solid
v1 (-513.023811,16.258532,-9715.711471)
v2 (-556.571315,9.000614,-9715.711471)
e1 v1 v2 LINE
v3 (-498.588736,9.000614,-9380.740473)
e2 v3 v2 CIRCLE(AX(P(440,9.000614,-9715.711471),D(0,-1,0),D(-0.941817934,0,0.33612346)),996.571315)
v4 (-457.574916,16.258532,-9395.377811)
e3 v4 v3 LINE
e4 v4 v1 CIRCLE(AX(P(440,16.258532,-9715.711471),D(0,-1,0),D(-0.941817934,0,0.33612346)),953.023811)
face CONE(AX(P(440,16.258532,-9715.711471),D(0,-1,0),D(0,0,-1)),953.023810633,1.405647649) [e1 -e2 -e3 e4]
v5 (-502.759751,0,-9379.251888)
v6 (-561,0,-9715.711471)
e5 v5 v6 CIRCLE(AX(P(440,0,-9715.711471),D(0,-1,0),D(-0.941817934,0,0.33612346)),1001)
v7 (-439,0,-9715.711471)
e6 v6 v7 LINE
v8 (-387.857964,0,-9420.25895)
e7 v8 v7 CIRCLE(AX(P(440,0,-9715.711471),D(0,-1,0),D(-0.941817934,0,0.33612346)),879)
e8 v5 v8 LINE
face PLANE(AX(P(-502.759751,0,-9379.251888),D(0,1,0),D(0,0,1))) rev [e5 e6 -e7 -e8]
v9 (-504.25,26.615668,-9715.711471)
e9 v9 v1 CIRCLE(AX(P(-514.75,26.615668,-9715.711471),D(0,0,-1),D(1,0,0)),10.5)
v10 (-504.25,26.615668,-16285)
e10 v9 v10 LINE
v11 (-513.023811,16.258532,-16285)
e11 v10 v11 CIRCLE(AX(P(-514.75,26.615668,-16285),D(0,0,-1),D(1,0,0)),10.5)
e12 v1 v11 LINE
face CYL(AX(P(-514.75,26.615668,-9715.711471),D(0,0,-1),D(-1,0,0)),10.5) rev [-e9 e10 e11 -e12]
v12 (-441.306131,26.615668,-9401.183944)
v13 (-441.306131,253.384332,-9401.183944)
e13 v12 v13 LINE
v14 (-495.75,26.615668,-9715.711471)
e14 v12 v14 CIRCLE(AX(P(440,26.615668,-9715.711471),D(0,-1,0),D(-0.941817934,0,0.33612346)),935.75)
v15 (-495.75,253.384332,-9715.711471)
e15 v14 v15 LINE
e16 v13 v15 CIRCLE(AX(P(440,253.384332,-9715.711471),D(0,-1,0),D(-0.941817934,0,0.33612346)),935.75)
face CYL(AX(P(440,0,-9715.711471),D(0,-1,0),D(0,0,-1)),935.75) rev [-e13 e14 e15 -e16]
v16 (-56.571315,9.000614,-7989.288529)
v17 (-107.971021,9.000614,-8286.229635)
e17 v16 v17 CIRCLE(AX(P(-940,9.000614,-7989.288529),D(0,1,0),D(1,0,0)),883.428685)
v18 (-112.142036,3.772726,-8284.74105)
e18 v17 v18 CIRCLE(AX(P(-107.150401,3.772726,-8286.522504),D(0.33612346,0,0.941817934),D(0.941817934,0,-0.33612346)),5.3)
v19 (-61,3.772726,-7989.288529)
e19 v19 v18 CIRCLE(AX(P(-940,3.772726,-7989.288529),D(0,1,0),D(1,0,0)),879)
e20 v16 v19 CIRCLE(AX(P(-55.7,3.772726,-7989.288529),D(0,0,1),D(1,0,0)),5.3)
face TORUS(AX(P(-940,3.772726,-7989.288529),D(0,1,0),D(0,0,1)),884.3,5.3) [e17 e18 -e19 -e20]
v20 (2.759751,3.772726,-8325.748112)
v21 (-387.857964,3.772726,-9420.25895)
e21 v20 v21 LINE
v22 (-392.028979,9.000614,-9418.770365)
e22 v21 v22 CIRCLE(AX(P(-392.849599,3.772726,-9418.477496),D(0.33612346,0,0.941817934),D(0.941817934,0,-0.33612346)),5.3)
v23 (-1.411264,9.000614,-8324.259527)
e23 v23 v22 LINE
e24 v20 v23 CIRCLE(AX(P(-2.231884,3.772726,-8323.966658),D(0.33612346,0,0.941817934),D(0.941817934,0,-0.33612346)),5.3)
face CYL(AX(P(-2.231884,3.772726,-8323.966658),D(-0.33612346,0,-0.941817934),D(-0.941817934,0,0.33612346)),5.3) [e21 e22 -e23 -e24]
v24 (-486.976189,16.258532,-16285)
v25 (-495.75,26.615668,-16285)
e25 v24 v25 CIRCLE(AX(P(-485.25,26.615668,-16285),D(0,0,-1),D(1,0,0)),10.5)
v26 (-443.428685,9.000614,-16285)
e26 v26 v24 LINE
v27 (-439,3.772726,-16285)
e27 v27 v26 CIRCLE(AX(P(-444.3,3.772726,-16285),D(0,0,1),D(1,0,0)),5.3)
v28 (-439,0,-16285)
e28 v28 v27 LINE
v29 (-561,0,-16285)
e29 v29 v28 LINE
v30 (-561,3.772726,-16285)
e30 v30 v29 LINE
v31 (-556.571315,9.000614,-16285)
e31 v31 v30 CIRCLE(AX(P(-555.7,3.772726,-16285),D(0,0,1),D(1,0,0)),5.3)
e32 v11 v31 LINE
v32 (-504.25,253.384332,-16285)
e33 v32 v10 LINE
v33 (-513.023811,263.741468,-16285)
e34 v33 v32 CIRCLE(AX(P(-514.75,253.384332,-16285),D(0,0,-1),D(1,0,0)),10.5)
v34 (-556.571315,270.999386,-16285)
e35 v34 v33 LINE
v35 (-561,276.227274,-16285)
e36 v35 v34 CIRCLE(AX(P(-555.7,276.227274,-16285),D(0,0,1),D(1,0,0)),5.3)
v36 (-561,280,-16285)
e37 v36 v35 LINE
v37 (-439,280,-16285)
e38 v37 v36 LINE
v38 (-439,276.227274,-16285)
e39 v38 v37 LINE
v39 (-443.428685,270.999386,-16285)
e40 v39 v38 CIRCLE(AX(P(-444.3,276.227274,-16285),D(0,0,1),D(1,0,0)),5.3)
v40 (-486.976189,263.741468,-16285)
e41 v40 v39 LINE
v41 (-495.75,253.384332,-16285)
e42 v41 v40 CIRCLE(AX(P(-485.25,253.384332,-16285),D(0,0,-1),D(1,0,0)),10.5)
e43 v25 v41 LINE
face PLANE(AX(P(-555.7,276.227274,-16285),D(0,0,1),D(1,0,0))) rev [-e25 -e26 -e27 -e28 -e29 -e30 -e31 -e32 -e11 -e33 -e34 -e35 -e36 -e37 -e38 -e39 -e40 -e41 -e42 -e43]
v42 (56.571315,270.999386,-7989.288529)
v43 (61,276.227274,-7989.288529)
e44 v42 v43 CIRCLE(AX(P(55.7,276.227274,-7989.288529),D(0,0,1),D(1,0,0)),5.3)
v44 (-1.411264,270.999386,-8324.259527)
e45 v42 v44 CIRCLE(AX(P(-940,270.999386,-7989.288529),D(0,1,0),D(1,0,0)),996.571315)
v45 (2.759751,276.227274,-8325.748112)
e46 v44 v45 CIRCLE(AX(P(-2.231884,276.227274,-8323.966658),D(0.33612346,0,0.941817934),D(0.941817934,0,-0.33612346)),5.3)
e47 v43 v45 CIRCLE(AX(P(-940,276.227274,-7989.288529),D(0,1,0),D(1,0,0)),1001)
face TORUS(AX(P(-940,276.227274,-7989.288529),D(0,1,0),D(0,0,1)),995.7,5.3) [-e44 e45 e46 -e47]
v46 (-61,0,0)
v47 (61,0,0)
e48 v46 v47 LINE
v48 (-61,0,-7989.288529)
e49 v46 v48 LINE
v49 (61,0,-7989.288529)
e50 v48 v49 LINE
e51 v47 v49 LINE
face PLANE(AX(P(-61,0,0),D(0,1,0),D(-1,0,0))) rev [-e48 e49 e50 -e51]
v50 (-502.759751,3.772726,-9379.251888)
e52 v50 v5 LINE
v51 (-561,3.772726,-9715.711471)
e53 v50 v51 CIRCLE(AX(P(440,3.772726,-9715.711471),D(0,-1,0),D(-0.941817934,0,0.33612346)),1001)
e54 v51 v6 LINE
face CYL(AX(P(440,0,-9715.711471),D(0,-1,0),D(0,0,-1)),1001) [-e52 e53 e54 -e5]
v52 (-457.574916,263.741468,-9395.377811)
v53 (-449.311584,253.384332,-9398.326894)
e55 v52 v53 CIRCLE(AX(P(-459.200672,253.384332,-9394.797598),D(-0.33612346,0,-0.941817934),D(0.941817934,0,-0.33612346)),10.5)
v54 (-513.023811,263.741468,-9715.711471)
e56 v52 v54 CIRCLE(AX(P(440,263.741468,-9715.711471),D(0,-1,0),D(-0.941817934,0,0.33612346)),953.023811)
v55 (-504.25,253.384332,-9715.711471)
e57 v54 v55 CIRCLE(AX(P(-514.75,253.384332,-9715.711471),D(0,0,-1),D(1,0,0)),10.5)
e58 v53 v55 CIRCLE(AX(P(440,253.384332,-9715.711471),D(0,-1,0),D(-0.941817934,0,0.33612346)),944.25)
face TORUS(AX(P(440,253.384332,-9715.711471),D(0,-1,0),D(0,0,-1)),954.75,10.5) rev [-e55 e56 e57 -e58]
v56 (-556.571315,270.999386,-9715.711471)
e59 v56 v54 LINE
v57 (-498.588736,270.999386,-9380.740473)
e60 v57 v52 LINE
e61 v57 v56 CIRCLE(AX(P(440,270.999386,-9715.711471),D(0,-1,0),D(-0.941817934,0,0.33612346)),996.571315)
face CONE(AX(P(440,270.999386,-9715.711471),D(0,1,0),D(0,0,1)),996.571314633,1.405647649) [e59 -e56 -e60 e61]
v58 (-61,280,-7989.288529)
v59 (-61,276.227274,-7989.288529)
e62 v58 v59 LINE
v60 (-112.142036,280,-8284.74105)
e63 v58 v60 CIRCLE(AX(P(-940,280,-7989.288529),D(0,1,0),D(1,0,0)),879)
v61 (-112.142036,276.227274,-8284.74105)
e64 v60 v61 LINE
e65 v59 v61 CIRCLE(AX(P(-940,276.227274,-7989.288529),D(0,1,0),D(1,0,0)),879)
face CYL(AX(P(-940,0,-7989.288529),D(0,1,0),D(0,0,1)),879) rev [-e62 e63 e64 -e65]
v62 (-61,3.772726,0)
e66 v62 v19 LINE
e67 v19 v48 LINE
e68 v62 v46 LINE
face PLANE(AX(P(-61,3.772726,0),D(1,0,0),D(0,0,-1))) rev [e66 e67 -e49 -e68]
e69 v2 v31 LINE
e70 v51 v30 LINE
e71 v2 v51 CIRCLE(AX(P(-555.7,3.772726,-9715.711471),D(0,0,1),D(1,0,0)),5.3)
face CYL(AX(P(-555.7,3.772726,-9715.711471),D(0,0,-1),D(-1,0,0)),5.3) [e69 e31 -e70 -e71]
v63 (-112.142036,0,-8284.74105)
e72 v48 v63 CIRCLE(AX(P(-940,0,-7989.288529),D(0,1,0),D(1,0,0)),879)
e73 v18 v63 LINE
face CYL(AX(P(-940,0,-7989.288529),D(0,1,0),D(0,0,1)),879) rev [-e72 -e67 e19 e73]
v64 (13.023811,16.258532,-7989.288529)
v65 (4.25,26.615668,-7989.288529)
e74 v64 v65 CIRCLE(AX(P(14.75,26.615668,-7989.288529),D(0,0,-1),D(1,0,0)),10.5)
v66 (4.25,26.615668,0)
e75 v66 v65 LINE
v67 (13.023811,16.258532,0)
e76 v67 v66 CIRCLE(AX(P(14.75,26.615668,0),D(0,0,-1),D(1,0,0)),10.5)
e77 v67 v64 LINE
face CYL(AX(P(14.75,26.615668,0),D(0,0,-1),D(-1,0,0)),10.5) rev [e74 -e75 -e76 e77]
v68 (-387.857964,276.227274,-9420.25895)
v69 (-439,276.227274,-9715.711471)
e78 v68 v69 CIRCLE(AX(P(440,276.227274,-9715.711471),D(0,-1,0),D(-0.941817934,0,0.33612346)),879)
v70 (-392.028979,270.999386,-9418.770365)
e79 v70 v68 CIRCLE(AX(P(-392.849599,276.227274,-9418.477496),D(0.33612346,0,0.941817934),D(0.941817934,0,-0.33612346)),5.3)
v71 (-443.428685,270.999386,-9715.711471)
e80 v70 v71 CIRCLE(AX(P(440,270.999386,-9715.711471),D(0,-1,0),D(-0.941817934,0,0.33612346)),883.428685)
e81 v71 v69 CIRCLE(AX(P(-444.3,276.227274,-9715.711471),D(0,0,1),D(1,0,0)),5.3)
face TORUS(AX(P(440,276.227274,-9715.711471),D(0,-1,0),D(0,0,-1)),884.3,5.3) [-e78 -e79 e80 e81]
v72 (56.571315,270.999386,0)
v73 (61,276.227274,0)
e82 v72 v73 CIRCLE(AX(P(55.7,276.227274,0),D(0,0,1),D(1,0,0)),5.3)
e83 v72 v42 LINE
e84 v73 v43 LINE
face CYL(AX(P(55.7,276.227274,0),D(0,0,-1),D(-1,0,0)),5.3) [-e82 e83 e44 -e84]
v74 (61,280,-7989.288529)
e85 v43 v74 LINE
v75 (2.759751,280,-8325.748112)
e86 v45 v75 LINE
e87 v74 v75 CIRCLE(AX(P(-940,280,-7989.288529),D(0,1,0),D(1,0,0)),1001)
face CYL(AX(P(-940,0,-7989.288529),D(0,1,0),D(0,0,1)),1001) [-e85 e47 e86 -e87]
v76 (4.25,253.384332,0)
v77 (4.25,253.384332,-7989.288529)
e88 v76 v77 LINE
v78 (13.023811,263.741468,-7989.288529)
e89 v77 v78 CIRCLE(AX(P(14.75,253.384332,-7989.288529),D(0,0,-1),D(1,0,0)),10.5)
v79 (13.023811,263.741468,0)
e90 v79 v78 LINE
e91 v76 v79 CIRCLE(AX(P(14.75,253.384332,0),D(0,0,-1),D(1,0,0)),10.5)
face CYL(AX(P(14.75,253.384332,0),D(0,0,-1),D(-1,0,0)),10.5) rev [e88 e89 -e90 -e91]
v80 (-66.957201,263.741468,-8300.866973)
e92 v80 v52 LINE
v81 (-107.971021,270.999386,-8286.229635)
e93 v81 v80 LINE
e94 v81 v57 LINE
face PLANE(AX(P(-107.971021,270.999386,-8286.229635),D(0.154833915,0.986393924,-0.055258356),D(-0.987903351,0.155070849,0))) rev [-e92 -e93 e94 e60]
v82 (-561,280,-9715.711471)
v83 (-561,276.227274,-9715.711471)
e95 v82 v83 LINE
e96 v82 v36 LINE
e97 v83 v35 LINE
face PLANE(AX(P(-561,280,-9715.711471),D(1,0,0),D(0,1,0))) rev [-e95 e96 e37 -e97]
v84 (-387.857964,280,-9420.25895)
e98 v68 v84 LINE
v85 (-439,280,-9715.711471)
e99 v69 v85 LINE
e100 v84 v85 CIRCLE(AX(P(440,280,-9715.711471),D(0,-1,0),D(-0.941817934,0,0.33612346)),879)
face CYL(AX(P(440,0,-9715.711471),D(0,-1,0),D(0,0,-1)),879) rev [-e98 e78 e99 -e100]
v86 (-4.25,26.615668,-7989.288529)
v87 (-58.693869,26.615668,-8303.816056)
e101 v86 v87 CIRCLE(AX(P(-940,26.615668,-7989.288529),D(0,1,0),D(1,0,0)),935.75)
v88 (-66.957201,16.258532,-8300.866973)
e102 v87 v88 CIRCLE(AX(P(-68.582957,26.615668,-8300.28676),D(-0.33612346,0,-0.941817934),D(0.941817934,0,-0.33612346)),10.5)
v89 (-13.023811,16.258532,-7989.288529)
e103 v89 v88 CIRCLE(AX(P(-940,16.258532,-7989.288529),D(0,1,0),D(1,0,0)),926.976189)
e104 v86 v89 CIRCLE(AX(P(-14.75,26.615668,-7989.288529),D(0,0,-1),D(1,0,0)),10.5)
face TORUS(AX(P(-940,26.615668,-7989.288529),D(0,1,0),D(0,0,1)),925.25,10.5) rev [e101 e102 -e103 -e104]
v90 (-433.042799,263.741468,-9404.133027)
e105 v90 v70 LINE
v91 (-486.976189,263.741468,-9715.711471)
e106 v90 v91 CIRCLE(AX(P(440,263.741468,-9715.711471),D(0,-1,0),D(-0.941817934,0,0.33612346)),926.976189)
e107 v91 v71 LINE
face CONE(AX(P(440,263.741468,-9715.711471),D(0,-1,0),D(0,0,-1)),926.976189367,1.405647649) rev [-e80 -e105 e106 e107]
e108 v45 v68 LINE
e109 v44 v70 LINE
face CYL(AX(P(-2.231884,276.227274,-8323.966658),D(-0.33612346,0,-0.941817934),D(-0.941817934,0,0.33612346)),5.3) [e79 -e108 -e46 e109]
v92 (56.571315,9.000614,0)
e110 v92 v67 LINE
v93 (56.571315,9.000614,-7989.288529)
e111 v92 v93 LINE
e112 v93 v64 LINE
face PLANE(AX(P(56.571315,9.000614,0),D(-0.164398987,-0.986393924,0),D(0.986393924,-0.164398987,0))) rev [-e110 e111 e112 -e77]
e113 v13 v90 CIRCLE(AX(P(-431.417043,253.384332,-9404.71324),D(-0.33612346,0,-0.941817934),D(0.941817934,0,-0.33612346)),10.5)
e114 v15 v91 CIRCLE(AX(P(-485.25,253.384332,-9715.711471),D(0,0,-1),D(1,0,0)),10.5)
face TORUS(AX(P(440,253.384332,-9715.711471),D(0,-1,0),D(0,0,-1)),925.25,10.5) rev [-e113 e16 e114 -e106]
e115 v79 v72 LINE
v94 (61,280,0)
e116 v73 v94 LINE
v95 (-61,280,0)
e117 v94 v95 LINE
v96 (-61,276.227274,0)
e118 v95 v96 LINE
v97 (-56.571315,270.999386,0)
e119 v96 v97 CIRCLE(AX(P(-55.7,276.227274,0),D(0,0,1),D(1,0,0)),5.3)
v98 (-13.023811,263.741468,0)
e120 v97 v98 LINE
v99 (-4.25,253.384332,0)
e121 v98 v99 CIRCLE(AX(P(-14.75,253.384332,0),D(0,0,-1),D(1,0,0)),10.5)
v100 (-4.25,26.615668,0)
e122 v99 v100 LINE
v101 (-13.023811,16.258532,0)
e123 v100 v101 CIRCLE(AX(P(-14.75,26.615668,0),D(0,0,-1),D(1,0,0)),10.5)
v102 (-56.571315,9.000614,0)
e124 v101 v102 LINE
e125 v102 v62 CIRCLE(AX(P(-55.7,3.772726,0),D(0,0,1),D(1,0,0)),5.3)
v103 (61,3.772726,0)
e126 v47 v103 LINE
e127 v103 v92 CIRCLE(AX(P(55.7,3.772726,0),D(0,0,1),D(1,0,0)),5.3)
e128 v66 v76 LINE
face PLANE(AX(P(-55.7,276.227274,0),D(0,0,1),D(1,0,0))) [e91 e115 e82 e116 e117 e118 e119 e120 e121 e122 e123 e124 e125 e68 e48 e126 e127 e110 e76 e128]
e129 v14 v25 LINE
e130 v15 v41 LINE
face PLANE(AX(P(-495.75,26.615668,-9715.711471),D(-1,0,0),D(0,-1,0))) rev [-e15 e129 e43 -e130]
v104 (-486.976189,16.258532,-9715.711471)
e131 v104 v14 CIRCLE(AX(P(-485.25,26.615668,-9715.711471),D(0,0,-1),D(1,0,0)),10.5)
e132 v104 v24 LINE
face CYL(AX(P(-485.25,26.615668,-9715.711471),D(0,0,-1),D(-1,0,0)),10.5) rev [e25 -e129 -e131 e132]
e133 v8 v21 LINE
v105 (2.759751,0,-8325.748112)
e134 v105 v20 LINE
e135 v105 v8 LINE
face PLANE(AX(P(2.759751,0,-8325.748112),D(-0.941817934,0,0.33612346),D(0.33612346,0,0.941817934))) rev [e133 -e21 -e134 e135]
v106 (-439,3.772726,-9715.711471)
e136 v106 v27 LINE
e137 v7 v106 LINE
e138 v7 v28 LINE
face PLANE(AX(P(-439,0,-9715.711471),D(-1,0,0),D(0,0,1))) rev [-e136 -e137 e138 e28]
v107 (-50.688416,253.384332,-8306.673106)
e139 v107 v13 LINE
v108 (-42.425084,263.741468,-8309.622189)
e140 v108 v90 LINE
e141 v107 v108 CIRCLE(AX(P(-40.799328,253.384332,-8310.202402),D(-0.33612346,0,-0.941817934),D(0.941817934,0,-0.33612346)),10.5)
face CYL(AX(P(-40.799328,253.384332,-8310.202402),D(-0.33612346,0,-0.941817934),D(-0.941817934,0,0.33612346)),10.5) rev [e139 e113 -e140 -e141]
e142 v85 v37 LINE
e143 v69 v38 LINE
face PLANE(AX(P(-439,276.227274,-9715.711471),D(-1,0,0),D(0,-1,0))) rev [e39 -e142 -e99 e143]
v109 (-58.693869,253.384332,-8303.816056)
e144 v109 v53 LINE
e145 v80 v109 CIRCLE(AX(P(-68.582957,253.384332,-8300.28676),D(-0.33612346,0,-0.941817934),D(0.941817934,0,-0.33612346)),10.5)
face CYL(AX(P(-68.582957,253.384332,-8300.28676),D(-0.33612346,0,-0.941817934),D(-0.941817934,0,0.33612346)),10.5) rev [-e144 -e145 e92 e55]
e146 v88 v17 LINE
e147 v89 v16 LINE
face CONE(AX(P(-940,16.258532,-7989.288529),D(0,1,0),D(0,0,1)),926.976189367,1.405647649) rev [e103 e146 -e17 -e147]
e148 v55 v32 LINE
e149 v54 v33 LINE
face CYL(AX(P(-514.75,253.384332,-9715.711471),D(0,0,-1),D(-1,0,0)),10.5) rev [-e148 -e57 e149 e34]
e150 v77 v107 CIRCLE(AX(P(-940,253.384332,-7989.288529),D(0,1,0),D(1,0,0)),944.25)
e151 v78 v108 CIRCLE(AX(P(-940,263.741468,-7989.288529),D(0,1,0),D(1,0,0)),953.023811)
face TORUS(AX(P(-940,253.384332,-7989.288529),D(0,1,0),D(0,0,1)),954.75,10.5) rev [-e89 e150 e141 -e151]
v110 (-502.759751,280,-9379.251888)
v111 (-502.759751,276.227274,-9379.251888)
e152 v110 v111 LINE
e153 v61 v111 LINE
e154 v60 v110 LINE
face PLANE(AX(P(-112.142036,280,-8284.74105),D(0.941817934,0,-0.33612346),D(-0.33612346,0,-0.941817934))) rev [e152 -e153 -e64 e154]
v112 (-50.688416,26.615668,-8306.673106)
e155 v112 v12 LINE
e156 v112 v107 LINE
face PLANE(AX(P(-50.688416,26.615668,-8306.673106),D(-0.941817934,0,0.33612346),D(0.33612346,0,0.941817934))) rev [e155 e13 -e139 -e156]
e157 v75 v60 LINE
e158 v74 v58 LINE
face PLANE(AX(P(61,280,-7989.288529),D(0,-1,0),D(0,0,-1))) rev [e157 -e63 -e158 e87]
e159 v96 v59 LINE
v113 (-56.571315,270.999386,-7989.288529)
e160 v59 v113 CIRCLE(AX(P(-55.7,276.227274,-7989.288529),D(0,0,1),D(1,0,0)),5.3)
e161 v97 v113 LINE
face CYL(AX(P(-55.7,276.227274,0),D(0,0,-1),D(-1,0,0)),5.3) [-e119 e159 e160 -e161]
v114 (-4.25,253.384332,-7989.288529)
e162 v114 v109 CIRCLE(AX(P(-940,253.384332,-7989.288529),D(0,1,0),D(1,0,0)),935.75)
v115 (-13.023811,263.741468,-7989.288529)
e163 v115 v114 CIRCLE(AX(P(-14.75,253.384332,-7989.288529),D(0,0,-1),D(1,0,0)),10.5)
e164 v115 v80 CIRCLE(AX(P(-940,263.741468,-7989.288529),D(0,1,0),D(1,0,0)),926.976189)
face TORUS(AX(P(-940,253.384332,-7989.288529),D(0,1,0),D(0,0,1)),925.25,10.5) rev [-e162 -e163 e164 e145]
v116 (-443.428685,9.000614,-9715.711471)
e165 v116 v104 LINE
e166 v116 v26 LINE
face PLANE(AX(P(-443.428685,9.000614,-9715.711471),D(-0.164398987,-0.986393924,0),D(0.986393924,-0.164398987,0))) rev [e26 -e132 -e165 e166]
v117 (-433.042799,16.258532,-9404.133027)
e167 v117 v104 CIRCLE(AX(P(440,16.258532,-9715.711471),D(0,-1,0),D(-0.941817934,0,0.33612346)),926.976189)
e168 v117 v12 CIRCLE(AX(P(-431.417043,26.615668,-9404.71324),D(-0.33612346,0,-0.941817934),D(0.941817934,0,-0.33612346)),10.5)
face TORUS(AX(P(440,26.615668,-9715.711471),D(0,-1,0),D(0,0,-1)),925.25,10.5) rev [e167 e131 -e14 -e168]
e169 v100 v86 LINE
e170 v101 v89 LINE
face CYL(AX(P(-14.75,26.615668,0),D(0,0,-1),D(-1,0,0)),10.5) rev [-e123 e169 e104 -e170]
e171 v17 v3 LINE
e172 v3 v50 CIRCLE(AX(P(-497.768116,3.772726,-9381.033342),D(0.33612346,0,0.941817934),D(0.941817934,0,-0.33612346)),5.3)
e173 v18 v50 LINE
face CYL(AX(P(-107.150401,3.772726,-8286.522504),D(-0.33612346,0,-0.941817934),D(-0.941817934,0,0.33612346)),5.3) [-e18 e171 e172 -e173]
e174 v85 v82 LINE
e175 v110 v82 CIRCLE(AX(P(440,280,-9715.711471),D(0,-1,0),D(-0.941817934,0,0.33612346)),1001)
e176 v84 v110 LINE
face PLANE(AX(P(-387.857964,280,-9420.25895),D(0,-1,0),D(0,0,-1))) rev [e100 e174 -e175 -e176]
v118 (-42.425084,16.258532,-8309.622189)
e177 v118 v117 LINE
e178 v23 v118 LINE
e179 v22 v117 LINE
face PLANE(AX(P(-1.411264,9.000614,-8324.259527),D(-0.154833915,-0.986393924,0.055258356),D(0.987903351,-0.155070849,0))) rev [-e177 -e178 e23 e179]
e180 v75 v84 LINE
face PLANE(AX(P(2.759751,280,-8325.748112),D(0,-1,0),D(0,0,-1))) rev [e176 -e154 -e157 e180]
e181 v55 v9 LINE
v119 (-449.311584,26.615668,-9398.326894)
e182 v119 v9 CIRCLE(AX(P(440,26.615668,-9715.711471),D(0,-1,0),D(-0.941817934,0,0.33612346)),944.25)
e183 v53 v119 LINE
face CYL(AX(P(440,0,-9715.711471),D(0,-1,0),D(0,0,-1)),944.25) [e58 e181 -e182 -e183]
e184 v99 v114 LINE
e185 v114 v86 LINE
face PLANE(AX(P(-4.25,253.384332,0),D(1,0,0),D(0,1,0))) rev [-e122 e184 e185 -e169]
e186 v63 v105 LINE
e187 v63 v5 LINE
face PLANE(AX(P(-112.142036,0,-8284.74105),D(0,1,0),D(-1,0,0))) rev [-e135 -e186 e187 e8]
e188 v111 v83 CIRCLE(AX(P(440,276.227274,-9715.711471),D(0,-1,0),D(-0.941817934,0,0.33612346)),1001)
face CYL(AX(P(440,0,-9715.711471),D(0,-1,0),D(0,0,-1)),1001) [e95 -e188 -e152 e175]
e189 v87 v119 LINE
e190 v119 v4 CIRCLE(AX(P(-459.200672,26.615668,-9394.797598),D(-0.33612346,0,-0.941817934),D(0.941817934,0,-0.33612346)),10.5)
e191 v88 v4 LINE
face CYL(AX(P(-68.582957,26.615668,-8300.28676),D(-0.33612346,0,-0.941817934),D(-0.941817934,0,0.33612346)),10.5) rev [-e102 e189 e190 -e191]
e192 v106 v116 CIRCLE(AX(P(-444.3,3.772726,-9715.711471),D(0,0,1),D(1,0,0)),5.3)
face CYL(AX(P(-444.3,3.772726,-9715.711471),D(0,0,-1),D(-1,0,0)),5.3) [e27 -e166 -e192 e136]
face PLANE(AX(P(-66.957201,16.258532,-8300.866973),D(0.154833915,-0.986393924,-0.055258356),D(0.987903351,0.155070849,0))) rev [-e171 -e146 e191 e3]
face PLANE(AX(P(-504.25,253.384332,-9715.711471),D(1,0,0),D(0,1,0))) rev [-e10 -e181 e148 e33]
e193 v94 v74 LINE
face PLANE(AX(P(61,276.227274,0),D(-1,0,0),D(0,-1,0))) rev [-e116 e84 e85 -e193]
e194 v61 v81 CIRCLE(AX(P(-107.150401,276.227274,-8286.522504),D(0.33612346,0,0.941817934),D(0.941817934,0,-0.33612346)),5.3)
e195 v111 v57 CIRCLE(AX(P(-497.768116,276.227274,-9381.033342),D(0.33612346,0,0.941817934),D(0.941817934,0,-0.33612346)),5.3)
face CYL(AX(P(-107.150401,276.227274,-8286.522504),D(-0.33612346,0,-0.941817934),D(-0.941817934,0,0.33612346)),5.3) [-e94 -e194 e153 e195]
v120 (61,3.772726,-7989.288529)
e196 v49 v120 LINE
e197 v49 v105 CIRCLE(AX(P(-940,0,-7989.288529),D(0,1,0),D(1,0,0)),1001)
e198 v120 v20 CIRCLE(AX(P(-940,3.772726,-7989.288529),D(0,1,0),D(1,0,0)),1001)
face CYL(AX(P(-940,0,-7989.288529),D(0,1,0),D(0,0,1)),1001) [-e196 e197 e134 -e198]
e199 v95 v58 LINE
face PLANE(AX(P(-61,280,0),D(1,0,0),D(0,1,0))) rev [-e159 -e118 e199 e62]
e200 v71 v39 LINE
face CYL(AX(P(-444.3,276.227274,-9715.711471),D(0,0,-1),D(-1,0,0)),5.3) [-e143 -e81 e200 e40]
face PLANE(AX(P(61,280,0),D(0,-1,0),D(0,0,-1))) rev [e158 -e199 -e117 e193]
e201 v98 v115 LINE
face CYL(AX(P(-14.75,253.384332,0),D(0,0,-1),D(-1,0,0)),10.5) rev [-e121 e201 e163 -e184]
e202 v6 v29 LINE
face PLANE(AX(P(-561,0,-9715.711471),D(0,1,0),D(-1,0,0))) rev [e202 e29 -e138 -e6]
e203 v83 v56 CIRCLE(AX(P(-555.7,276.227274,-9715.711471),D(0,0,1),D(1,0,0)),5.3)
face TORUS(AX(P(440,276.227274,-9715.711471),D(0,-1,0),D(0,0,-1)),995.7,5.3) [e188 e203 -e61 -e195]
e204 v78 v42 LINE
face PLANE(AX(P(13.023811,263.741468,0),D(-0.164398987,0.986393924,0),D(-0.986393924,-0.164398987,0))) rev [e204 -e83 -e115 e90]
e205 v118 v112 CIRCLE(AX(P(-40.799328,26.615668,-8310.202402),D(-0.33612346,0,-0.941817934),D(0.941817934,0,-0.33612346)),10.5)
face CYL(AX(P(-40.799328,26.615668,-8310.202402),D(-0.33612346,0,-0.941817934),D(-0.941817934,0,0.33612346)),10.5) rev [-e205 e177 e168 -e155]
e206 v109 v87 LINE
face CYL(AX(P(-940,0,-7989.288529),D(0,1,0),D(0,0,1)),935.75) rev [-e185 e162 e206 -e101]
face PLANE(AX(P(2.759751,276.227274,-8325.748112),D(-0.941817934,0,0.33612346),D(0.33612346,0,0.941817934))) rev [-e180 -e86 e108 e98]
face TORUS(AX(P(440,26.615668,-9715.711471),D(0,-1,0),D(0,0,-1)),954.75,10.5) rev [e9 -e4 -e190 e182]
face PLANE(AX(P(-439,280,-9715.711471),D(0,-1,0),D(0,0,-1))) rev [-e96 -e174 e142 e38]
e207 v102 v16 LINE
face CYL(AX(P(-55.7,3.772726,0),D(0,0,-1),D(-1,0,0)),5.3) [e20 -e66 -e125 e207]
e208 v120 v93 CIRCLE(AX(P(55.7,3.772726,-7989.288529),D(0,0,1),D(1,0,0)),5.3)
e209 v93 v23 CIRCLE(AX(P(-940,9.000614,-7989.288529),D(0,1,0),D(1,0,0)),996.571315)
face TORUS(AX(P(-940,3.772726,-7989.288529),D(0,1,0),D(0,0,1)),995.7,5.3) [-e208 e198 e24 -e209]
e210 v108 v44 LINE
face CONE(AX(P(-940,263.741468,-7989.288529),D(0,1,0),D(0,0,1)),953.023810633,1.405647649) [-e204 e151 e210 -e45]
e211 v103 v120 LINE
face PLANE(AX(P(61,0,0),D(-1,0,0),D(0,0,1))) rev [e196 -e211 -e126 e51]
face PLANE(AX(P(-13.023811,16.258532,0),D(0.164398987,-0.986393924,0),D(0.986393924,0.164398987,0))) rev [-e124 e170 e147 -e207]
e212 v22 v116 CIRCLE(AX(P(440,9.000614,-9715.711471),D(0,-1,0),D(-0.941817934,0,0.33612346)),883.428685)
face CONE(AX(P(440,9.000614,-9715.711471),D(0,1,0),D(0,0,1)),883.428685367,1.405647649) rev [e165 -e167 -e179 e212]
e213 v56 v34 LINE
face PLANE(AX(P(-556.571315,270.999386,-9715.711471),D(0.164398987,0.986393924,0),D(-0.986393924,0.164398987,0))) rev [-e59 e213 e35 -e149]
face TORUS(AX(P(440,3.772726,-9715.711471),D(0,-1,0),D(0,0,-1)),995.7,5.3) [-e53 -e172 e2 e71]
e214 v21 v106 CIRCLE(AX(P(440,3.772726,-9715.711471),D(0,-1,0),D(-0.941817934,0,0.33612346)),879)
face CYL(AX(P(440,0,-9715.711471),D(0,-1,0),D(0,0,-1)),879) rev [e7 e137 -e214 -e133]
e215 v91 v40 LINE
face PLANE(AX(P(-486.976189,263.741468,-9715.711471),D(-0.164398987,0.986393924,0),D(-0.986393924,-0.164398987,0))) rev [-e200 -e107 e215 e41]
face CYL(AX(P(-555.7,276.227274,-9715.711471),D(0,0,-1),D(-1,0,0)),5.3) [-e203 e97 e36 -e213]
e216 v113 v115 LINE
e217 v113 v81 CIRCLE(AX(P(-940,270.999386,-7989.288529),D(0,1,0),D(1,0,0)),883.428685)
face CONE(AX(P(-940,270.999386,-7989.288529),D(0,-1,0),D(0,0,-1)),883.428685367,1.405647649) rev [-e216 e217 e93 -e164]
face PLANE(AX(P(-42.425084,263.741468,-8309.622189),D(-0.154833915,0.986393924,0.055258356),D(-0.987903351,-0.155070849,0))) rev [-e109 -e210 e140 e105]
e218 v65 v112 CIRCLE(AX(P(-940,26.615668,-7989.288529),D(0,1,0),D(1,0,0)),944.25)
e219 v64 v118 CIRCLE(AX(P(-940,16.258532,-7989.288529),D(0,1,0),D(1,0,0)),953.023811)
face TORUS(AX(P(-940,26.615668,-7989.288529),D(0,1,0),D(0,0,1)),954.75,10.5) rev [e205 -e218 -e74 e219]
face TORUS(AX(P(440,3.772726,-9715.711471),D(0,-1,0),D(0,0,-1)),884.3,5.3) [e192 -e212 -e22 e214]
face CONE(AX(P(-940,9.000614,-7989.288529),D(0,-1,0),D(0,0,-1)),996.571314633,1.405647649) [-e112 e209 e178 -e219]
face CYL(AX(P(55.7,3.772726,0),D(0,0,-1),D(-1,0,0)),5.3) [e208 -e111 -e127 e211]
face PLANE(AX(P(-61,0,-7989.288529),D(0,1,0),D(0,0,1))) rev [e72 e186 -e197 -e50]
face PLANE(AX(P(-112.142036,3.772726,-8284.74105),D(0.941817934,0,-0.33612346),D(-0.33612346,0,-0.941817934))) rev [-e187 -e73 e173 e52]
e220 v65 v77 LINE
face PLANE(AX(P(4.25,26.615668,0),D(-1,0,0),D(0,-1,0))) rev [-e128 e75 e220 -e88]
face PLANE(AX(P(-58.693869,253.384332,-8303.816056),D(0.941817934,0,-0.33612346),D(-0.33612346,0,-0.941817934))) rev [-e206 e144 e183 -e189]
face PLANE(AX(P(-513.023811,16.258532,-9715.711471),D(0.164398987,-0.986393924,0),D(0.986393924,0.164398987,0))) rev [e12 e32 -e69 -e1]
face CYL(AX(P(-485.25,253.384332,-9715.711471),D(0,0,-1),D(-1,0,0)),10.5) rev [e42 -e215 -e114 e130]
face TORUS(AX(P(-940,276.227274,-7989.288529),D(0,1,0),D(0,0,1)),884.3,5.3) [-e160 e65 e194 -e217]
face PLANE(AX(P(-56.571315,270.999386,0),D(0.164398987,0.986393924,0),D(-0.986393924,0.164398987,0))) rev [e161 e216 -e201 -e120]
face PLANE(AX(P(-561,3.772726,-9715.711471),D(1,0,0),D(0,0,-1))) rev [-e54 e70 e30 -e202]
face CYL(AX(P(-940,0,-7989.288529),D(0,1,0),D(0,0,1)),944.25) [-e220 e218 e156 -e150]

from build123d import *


with BuildPart() as part:
    # Sweep1: sweep along a path in Sketch2
    with BuildLine(Plane(origin=(0, 0, 0), x_dir=(1, 0, 0), z_dir=(0, 1, 0))) as sweep1_path:
        Line((0, 0), (0, 7989.288529227))
        ThreePointArc((0, 7989.288529227), (-13.773697715, 8149.615809986), (-54.691142459, 8305.244581169))
        Line((-54.691142459, 8305.244581169), (-445.308857541, 9399.755418831))
        ThreePointArc((-445.308857541, 9399.755418831), (-486.226302285, 9555.384190014), (-500, 9715.711470773))
        Line((-500, 9715.711470773), (-500, 16285))
    # Sketch1 → Sweep1 (sweep)
    with BuildSketch(Plane.XY):
        with BuildLine():
            Line((-61, 280), (-61, 276.227273568))
            ThreePointArc((-61, 276.227273568), (-59.744005907, 272.801486619), (-56.571314633, 270.999385772))
            Line((-56.571314633, 270.999385772), (-13.023810633, 263.741468439))
            ThreePointArc((-13.023810633, 263.741468439), (-6.738290184, 260.171268648), (-4.25, 253.384332239))
            Line((-4.25, 253.384332239), (-4.25, 26.615667761))
            ThreePointArc((-4.25, 26.615667761), (-6.738290184, 19.828731352), (-13.023810633, 16.258531561))
            Line((-13.023810633, 16.258531561), (-56.571314633, 9.000614228))
            ThreePointArc((-56.571314633, 9.000614228), (-59.744005907, 7.198513381), (-61, 3.772726432))
            Line((-61, 3.772726432), (-61, 0))
            Line((-61, 0), (61, 0))
            Line((61, 0), (61, 3.772726432))
            ThreePointArc((61, 3.772726432), (59.744005907, 7.198513381), (56.571314633, 9.000614228))
            Line((56.571314633, 9.000614228), (13.023810633, 16.258531561))
            ThreePointArc((13.023810633, 16.258531561), (6.738290184, 19.828731352), (4.25, 26.615667761))
            Line((4.25, 26.615667761), (4.25, 253.384332239))
            ThreePointArc((4.25, 253.384332239), (6.738290184, 260.171268648), (13.023810633, 263.741468439))
            Line((13.023810633, 263.741468439), (56.571314633, 270.999385772))
            ThreePointArc((56.571314633, 270.999385772), (59.744005907, 272.801486619), (61, 276.227273568))
            Line((61, 276.227273568), (61, 280))
            Line((61, 280), (-61, 280))
        make_face()
    sweep(path=sweep1_path.line)


solid = part.part
